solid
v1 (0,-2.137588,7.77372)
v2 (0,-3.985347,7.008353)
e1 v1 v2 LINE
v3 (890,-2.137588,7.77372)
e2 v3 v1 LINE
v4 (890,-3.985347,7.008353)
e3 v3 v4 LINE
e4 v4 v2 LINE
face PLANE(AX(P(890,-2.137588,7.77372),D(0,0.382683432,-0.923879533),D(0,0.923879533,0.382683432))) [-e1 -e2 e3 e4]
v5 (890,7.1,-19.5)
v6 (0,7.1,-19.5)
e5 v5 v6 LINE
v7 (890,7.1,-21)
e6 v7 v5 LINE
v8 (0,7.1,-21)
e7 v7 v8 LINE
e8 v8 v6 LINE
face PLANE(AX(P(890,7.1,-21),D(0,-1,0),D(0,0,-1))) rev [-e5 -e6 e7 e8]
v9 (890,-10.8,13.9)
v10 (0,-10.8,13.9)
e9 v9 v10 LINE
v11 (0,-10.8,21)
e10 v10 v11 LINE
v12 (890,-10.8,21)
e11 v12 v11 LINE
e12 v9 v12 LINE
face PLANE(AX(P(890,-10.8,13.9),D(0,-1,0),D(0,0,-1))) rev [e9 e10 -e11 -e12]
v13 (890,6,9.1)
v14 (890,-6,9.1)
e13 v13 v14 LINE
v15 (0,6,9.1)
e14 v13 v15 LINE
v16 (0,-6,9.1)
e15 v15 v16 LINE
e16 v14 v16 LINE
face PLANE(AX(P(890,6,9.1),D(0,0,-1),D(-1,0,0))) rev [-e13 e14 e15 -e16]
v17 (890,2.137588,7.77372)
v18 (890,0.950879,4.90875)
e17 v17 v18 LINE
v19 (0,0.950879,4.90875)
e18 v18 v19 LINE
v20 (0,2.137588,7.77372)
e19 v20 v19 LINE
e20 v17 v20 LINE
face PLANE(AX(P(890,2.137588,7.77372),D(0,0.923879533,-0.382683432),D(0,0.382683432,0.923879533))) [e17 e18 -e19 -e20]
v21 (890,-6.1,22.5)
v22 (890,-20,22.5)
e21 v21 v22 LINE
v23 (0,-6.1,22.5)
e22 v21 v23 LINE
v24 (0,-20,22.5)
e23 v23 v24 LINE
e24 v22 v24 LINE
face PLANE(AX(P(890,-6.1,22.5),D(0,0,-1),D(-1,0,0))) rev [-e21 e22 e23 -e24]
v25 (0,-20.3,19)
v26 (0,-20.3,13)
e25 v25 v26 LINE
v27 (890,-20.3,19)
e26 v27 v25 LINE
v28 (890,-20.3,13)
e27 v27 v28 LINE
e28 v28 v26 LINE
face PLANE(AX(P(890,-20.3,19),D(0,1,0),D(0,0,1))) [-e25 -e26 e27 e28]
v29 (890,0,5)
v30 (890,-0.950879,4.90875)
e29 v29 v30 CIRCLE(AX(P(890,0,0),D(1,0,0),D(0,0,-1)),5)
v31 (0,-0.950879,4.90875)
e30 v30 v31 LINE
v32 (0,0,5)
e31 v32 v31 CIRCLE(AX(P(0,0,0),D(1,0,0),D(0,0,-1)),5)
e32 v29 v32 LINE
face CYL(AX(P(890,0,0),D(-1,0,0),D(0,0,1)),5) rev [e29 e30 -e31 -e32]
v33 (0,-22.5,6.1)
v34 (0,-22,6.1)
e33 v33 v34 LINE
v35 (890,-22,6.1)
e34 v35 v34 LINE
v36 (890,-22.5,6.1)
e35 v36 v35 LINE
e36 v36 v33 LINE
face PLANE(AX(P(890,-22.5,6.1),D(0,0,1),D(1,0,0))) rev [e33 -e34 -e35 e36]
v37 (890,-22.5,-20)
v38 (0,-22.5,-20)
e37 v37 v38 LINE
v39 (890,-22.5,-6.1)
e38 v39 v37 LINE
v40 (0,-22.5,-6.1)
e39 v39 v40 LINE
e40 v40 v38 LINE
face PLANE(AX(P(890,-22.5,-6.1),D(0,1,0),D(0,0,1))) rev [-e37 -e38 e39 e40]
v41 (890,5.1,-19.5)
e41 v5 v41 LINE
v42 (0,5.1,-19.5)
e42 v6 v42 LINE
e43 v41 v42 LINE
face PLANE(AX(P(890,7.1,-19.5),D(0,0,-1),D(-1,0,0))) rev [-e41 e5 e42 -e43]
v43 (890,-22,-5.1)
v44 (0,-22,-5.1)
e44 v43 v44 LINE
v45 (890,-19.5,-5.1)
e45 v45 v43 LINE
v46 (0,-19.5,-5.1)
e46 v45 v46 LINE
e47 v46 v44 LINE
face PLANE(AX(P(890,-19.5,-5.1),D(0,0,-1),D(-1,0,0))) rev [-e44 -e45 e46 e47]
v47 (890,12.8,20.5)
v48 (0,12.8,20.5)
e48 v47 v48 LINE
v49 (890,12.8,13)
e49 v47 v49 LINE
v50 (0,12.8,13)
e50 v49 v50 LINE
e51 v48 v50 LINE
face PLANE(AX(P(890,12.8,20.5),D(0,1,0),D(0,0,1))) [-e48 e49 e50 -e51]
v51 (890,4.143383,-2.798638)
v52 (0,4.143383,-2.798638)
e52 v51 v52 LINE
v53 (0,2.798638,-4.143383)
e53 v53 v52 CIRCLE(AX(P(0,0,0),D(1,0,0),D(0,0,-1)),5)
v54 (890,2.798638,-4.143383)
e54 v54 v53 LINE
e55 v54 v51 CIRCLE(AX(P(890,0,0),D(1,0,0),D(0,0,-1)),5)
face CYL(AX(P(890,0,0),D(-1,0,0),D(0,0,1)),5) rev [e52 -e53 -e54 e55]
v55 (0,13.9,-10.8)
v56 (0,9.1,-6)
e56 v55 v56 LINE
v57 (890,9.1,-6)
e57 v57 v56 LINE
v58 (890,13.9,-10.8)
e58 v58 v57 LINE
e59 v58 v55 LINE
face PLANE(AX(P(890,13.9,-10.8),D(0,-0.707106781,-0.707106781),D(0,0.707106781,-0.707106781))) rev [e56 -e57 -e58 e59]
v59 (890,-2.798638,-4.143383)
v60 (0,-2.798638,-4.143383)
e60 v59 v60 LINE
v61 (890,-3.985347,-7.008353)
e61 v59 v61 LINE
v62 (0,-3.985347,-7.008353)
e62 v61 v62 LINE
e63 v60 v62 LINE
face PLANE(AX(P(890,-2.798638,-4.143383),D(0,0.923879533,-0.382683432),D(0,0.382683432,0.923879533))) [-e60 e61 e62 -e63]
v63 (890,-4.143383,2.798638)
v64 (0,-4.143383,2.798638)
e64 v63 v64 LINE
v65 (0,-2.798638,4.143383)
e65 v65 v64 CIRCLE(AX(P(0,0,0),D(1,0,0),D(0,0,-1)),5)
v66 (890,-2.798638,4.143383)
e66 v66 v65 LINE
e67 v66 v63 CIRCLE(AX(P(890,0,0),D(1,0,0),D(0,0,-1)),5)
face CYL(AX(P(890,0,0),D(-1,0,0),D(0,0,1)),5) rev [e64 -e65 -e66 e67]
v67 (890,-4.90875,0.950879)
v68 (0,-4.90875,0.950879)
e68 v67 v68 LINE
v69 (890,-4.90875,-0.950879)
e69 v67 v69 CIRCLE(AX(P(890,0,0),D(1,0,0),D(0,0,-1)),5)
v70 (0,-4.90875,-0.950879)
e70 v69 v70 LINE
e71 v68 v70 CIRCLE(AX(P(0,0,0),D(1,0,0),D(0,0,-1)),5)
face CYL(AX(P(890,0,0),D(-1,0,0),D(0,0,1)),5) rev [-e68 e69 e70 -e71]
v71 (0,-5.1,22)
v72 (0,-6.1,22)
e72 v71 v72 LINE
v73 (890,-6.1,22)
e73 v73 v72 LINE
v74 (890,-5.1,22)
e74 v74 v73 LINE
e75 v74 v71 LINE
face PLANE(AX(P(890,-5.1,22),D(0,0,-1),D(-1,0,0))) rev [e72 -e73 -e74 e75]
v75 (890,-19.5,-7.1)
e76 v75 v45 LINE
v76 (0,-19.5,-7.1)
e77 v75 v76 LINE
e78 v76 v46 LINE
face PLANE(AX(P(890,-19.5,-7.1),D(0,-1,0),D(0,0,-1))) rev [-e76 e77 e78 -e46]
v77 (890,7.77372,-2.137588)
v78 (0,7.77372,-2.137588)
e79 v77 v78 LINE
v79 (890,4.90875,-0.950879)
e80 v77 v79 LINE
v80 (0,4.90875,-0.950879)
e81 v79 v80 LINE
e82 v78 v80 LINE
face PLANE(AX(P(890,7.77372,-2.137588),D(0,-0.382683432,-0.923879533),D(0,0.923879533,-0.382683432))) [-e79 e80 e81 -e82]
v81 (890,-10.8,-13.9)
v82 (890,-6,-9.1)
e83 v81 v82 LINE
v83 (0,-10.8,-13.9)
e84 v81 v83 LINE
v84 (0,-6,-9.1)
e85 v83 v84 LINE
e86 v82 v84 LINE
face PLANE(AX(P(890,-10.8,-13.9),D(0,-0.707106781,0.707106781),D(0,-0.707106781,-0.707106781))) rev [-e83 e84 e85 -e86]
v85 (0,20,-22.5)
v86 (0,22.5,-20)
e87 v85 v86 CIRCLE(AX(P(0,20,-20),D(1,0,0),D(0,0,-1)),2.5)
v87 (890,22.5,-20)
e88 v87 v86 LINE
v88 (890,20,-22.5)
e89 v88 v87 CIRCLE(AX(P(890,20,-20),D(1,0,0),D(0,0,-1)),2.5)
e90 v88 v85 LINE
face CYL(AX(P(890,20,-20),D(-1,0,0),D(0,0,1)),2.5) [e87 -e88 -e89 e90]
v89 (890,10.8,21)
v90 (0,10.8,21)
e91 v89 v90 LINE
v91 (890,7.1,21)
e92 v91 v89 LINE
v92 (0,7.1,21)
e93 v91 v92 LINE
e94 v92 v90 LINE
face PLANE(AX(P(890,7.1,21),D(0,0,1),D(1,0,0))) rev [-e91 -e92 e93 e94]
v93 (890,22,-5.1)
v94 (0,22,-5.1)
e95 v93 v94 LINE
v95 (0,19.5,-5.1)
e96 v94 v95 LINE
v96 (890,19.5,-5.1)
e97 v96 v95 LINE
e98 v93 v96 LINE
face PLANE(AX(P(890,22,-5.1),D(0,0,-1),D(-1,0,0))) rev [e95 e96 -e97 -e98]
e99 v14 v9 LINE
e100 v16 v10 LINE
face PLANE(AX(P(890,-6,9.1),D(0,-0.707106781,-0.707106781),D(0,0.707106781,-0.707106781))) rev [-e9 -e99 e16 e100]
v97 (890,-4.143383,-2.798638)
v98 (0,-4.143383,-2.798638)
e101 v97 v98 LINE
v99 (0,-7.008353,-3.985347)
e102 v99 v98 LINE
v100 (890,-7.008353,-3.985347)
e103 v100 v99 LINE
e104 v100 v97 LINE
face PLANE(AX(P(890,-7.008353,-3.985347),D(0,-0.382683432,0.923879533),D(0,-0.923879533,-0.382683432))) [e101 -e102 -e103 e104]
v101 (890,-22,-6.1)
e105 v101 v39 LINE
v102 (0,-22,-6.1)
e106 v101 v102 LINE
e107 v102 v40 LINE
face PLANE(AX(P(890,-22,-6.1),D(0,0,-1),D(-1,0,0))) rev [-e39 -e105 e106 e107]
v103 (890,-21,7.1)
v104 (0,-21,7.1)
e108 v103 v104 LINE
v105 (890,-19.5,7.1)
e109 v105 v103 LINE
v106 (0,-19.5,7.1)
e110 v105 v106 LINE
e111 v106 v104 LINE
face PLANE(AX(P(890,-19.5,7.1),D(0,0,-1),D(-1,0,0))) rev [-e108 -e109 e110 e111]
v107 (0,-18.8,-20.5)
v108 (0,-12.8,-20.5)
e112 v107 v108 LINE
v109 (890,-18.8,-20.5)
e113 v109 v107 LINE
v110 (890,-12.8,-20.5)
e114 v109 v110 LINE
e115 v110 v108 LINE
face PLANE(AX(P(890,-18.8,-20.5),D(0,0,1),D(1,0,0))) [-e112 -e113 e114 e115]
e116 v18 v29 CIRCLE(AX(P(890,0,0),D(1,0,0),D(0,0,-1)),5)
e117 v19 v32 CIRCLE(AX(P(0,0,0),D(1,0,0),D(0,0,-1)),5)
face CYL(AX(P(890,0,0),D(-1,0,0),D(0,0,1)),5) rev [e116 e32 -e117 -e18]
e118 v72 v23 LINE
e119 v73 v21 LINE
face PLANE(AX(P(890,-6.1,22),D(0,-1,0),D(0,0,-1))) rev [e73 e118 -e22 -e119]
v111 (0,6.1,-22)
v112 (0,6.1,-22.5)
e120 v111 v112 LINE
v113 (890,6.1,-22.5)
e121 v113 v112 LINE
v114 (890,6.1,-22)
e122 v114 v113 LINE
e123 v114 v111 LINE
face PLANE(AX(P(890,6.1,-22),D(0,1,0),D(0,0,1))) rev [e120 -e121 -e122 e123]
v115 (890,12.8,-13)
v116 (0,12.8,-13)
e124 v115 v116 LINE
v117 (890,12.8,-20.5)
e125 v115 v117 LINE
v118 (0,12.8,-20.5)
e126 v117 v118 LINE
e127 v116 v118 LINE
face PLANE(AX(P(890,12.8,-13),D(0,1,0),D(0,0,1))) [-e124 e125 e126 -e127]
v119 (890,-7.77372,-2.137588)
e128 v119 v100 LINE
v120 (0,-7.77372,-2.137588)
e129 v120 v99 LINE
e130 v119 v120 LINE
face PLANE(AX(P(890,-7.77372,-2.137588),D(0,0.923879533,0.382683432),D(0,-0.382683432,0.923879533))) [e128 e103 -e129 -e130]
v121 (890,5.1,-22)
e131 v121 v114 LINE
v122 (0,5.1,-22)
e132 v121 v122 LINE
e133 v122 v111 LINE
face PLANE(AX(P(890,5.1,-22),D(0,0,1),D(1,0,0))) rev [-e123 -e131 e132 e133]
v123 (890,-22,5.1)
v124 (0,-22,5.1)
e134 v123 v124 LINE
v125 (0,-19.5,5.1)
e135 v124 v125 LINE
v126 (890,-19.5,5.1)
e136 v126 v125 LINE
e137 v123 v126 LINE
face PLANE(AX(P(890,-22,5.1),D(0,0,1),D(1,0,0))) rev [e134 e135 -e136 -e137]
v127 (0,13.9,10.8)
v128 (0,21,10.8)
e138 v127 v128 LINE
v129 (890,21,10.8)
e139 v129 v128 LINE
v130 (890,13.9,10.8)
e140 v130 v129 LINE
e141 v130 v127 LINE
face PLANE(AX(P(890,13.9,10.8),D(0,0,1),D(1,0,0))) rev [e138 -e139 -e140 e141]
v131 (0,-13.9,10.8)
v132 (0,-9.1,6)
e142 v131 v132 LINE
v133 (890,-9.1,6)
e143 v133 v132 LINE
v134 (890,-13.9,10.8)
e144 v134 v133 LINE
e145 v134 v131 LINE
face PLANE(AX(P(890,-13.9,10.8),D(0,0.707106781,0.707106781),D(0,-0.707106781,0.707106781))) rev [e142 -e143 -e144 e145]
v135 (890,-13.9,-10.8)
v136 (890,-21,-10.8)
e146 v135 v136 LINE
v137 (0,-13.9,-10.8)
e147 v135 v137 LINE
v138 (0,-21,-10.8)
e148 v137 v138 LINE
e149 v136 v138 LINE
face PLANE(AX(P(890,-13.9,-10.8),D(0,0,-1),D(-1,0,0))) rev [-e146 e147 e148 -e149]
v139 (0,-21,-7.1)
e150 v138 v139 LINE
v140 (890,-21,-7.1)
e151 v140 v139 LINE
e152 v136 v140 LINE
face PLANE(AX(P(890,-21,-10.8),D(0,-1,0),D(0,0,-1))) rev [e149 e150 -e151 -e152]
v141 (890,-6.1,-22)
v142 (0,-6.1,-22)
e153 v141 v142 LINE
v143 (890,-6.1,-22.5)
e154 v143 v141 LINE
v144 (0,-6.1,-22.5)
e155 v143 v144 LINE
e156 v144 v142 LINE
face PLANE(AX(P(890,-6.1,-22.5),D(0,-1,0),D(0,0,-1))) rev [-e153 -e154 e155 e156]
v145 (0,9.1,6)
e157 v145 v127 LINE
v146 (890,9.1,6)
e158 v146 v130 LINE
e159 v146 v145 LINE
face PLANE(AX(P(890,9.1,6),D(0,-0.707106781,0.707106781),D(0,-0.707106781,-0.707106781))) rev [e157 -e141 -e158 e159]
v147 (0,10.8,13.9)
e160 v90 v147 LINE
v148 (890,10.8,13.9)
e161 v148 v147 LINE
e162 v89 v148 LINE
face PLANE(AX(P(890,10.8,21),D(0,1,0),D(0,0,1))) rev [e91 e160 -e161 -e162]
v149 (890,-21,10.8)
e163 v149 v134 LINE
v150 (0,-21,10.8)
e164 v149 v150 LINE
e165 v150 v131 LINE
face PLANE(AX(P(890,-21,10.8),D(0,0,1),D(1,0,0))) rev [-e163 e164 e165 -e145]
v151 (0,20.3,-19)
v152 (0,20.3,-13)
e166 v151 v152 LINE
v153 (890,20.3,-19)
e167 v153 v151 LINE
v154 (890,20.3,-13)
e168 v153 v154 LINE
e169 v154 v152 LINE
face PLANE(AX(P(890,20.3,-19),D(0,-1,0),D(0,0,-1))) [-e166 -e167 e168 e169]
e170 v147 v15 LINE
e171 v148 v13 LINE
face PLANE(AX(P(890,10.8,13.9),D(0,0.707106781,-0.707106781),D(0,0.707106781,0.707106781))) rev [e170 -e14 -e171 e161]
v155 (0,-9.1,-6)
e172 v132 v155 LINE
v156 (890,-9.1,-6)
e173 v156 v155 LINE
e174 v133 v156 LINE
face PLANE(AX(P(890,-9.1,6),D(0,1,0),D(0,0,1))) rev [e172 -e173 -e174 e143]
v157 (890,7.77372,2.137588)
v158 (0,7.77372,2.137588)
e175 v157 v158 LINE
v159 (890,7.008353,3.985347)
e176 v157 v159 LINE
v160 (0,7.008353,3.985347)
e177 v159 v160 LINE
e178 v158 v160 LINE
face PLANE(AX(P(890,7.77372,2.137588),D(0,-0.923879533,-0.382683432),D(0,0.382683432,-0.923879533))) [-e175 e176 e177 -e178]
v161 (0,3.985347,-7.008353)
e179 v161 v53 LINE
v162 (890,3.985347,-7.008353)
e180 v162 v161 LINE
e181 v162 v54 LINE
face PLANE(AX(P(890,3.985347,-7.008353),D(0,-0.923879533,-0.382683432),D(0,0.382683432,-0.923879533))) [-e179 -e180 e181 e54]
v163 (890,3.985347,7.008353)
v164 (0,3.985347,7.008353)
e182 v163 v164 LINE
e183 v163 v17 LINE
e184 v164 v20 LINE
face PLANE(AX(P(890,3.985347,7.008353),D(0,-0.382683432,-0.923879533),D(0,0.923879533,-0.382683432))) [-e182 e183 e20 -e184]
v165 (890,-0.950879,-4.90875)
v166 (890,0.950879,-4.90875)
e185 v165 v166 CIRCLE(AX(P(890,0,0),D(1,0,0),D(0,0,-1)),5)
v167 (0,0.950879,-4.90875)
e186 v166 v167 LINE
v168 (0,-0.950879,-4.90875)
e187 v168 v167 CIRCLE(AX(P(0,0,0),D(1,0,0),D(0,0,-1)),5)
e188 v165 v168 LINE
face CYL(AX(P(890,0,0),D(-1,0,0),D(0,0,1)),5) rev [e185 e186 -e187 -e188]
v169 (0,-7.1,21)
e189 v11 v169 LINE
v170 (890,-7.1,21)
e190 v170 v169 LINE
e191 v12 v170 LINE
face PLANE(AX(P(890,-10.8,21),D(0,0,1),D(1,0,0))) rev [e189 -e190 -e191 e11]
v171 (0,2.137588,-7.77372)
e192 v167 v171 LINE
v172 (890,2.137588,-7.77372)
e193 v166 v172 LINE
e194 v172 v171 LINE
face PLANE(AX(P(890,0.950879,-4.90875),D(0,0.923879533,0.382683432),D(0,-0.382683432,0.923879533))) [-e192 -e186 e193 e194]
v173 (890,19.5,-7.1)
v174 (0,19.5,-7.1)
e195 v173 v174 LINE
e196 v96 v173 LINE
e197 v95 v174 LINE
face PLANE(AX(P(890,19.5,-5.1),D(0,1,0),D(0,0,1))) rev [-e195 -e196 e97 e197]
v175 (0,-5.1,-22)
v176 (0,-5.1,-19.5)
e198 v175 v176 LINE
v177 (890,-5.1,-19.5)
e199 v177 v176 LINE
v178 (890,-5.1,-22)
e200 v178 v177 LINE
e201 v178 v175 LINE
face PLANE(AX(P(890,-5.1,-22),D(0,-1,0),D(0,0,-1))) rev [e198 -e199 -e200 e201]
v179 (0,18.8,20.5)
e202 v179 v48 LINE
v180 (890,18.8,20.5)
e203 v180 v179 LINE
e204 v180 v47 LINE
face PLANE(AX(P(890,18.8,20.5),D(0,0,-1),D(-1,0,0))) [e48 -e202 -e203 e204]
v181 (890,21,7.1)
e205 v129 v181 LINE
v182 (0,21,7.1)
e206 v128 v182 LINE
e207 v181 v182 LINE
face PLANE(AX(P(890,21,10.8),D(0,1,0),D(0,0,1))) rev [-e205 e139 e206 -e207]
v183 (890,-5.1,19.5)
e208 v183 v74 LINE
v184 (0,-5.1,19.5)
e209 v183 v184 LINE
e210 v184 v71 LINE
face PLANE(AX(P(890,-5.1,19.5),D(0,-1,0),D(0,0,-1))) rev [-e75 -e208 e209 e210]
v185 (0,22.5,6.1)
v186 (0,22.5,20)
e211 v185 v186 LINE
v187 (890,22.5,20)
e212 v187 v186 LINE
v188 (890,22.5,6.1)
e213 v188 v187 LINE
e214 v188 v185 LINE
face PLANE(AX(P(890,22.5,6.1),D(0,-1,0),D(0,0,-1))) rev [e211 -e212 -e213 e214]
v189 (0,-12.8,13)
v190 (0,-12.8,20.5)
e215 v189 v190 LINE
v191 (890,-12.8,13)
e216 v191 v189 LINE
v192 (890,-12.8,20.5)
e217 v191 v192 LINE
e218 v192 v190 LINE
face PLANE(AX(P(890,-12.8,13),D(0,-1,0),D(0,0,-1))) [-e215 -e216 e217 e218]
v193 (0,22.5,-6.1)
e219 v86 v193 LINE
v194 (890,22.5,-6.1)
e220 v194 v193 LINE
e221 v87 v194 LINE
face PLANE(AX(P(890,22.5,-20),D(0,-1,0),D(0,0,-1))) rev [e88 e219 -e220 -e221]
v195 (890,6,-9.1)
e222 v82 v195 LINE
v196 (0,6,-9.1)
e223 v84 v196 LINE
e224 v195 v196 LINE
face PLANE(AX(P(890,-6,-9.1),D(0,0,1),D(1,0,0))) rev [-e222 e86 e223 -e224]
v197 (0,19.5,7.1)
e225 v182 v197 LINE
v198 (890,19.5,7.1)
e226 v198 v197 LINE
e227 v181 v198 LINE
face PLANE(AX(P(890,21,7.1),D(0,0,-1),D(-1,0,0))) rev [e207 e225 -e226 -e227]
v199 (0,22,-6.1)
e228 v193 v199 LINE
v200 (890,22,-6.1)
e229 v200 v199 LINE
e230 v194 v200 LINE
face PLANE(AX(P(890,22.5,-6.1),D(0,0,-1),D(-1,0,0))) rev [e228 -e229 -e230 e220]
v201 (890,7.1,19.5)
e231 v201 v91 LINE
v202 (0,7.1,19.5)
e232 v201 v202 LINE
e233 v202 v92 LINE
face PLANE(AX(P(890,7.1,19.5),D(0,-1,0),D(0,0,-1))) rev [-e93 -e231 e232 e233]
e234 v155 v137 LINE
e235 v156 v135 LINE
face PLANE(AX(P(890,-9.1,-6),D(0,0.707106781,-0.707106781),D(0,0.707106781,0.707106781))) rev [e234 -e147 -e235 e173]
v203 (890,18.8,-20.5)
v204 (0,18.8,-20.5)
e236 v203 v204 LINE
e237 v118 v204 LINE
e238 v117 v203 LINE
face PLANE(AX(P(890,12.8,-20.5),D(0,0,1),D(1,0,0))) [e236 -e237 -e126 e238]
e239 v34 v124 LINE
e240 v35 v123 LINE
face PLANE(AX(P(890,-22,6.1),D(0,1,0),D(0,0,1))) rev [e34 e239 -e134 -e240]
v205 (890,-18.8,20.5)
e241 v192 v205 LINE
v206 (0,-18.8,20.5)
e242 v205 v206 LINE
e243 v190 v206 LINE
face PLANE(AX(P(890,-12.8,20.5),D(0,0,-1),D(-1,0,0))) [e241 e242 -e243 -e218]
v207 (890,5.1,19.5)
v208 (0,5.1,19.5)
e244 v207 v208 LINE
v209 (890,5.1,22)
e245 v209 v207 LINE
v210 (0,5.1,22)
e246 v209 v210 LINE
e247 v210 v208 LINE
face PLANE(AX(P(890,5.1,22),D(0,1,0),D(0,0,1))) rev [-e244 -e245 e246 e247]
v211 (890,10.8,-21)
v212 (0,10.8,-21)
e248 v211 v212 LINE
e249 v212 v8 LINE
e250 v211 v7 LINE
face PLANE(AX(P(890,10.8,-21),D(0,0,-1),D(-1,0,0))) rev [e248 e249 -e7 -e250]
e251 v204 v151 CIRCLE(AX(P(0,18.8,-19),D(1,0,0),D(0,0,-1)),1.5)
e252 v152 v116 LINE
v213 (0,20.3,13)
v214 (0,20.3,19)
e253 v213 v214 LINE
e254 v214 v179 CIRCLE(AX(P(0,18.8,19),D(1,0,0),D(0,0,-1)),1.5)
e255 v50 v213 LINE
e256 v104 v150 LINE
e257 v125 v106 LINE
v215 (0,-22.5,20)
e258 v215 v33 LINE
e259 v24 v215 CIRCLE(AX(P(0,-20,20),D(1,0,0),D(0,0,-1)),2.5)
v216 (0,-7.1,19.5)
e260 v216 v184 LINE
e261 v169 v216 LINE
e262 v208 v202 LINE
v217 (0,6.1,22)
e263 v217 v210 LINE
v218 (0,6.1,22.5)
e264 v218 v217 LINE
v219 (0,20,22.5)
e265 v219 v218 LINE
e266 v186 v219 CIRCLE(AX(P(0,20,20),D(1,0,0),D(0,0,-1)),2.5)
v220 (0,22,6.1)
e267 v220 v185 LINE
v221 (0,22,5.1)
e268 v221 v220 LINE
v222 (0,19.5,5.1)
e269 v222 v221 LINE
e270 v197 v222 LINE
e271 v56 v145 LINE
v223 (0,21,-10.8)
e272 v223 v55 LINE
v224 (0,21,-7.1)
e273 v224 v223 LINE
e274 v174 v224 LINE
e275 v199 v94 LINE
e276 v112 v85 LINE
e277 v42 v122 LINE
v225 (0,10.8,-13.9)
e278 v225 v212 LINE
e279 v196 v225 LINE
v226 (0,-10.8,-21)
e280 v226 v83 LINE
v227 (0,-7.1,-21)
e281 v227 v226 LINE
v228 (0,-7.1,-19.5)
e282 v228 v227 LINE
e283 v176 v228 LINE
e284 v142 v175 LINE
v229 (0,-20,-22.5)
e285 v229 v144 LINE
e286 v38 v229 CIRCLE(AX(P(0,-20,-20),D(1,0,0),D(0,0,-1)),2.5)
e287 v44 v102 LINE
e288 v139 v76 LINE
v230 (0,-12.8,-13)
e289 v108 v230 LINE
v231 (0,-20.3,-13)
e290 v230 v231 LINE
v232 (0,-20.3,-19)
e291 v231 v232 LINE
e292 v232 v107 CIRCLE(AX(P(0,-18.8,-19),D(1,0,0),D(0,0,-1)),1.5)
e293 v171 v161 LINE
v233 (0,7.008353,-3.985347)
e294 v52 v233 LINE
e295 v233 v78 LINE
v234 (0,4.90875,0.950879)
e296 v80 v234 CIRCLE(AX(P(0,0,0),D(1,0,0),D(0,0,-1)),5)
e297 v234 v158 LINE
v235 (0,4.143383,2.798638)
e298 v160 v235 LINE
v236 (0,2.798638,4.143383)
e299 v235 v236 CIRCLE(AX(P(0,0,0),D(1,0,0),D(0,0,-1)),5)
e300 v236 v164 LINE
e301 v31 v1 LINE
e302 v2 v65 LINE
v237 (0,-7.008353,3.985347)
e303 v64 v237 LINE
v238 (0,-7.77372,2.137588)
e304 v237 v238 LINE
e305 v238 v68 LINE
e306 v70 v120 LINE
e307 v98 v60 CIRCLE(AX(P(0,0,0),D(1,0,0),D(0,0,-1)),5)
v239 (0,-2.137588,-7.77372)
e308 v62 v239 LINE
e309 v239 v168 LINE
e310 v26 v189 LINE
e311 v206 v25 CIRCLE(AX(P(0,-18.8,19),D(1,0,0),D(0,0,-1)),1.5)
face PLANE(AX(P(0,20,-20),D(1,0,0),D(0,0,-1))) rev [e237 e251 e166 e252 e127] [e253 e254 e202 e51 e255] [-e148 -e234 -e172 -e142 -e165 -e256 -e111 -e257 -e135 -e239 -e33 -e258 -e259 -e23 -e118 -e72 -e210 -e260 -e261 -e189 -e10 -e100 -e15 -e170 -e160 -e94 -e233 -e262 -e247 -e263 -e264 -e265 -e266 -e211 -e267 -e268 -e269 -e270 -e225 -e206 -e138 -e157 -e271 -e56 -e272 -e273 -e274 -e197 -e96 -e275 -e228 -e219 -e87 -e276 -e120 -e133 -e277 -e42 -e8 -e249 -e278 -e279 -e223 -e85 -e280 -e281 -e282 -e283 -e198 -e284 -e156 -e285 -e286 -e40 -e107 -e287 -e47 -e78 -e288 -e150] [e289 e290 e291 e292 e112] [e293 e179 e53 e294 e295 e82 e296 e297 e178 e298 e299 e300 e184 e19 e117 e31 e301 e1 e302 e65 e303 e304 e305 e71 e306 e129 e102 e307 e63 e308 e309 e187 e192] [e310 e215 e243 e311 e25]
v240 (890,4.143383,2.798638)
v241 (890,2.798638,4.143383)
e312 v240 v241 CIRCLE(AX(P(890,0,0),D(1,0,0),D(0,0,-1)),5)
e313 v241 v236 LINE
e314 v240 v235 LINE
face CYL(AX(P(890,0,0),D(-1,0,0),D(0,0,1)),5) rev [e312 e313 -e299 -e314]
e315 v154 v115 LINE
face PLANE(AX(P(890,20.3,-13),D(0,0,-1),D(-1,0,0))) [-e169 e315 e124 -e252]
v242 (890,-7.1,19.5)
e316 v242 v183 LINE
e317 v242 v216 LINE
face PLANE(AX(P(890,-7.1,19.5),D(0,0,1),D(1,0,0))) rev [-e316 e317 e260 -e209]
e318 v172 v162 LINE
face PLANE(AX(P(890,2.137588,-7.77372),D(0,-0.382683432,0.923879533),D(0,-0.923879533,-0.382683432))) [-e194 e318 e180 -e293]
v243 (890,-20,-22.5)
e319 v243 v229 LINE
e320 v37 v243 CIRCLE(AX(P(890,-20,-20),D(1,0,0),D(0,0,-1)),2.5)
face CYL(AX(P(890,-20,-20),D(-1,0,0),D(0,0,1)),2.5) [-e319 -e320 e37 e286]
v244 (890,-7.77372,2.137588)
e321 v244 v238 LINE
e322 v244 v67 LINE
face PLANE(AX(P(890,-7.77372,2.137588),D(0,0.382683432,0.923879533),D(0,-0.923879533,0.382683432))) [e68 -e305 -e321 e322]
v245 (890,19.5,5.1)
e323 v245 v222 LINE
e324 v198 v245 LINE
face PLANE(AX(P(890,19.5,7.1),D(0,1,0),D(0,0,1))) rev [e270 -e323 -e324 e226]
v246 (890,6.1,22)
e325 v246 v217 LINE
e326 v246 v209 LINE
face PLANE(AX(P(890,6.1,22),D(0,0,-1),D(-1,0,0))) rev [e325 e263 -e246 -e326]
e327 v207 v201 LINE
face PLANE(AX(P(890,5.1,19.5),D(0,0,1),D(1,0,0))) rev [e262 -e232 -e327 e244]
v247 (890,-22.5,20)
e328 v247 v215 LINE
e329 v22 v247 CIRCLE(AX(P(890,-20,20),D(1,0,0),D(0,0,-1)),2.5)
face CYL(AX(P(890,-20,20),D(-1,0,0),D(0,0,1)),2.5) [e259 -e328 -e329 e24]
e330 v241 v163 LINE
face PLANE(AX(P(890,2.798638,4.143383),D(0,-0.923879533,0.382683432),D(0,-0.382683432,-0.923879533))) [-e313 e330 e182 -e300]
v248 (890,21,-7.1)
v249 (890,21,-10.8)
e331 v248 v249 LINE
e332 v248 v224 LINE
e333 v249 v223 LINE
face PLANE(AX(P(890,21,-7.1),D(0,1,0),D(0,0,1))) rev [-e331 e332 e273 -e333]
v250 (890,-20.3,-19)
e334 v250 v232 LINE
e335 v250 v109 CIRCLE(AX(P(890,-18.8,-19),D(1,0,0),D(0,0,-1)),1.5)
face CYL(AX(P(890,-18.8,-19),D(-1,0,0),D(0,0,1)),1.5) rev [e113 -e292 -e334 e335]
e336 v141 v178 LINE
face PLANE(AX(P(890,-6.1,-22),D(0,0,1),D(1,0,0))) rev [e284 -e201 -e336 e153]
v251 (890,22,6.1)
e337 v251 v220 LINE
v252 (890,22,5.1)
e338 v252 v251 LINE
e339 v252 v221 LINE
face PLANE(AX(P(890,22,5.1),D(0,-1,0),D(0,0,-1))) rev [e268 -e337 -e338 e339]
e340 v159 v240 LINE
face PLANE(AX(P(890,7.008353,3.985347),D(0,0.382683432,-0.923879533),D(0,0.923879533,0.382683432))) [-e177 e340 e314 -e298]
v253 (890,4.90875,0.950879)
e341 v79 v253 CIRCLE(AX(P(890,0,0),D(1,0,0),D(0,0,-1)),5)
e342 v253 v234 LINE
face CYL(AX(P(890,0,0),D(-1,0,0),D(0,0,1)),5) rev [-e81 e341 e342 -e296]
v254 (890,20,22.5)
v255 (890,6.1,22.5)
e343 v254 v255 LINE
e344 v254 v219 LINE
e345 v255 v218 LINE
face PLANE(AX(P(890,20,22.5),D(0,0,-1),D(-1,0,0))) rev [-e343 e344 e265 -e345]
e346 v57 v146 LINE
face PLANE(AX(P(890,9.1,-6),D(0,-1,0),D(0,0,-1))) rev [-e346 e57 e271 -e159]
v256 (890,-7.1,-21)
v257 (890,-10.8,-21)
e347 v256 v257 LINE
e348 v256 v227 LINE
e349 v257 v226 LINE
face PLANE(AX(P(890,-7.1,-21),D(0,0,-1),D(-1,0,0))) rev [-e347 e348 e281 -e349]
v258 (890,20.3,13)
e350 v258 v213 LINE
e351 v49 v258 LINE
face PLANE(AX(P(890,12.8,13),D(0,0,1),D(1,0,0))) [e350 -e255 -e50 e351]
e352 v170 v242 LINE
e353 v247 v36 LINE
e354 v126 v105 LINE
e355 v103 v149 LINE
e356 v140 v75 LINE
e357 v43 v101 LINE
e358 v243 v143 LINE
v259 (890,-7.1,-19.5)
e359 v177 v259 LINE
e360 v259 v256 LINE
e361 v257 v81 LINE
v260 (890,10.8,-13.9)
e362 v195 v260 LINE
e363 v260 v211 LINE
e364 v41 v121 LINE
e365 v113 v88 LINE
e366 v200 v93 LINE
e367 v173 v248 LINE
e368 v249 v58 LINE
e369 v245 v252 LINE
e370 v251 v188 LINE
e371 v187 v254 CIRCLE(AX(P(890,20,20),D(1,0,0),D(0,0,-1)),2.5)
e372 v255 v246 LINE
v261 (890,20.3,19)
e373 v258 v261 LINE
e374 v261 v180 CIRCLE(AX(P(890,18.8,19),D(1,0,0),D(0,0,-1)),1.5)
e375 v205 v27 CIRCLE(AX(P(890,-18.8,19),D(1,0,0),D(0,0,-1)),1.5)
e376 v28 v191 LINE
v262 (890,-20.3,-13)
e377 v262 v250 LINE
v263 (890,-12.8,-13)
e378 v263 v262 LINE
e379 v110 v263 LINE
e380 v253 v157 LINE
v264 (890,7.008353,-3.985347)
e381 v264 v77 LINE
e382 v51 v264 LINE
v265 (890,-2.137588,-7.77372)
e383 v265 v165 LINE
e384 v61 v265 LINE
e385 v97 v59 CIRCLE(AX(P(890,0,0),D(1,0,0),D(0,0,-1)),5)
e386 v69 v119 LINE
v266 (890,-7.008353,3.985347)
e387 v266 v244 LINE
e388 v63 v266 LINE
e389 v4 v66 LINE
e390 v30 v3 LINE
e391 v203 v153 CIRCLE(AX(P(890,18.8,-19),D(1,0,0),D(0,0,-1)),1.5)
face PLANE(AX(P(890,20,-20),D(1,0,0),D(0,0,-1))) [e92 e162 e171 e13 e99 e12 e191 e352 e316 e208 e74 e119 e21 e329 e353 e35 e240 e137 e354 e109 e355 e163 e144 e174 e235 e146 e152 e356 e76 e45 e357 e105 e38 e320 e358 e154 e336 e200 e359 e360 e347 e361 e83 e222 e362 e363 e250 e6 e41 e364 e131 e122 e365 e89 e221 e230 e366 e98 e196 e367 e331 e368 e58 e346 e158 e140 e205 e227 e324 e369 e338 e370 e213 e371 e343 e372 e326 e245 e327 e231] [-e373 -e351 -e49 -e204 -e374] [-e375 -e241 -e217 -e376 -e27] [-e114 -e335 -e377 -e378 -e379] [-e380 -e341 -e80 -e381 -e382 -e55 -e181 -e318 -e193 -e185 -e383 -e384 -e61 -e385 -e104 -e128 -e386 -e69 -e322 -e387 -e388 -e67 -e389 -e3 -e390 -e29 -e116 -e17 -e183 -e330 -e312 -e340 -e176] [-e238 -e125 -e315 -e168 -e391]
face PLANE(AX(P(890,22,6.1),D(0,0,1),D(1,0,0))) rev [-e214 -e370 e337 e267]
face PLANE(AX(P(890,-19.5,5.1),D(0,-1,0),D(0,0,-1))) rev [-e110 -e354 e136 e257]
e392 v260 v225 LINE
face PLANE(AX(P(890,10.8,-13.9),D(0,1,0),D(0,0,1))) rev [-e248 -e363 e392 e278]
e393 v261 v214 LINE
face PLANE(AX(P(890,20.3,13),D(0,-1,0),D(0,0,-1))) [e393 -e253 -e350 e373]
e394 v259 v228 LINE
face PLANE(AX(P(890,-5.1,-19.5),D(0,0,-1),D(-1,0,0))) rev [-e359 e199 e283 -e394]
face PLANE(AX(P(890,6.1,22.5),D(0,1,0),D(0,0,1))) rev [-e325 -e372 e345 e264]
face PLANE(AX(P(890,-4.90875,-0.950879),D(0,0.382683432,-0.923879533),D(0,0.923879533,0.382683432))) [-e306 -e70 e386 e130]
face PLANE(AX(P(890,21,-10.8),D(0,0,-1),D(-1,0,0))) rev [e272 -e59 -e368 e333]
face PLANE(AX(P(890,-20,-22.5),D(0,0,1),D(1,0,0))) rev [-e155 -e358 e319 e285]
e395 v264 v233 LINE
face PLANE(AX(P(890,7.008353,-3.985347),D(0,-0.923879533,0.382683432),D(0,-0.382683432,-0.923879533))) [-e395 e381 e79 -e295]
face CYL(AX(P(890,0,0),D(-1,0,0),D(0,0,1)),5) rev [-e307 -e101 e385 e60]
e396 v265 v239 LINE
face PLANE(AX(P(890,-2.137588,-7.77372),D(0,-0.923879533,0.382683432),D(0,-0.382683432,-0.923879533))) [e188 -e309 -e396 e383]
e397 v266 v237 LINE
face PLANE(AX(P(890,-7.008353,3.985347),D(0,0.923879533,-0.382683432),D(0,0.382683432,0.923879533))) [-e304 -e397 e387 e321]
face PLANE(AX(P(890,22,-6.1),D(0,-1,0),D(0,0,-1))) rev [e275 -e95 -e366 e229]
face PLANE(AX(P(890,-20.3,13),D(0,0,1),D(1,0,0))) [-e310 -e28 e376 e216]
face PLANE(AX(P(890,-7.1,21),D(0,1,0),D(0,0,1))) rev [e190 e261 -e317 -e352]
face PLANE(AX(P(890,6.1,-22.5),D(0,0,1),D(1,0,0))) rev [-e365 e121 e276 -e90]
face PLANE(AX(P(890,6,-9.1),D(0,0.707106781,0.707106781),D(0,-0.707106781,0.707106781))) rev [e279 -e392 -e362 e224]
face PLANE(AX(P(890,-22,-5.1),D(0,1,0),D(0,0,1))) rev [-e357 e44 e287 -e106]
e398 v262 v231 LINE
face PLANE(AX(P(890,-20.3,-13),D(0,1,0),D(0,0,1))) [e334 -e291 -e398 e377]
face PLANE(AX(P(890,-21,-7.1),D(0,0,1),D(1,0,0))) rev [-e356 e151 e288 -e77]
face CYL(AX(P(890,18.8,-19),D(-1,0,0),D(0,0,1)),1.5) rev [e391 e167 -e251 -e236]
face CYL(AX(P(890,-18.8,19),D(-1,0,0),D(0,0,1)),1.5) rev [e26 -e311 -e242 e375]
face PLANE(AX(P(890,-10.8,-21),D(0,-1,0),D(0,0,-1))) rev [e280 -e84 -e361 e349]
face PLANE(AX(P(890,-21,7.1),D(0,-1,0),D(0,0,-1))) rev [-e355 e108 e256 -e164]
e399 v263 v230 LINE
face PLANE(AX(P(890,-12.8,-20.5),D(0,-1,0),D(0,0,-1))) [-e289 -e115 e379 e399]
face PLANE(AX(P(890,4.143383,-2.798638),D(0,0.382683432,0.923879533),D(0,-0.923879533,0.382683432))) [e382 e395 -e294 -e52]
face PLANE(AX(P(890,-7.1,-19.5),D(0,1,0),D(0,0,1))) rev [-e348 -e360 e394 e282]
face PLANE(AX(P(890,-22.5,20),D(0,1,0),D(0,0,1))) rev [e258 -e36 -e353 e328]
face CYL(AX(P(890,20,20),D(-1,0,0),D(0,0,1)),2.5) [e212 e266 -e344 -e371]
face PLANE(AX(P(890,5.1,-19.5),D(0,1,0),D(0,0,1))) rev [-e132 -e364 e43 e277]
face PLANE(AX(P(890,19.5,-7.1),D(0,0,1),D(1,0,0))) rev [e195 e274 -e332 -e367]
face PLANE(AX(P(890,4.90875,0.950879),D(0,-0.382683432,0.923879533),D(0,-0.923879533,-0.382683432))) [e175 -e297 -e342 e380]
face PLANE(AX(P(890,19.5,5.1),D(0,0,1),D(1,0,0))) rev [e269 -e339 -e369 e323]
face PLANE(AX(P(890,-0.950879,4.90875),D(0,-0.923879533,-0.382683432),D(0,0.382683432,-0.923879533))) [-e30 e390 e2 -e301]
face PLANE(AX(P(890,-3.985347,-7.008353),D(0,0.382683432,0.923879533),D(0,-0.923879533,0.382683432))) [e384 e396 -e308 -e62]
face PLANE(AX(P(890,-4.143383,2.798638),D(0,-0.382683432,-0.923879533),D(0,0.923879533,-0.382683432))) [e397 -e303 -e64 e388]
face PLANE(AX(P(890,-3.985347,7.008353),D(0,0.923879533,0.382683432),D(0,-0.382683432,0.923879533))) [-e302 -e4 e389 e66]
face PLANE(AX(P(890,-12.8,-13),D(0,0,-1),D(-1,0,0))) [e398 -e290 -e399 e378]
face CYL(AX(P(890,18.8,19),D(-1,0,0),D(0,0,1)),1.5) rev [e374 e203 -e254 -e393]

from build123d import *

# Parameters (mm, degrees)
ALUMINUM_PROFILE_45_X_45L_X_R2_5_1_DEPTH = 890


with BuildPart() as part:
    # Sketch1 → Aluminum Profile 45 X 45L X R2.5(1) (new body)
    with BuildSketch(Plane.YZ):
        with BuildLine():
            Line((6.1, -22.5), (20, -22.5))
            ThreePointArc((20, -22.5), (21.767766953, -21.767766953), (22.5, -20))
            Line((22.5, -20), (22.5, -6.1))
            Line((22.5, -6.1), (22, -6.1))
            Line((22, -6.1), (22, -5.1))
            Line((22, -5.1), (19.5, -5.1))
            Line((19.5, -5.1), (19.5, -7.1))
            Line((19.5, -7.1), (21, -7.1))
            Line((21, -7.1), (21, -10.8))
            Line((21, -10.8), (13.9, -10.8))
            Line((13.9, -10.8), (9.1, -6))
            Line((9.1, -6), (9.1, 6))
            Line((9.1, 6), (13.9, 10.8))
            Line((13.9, 10.8), (21, 10.8))
            Line((21, 10.8), (21, 7.1))
            Line((21, 7.1), (19.5, 7.1))
            Line((19.5, 7.1), (19.5, 5.1))
            Line((19.5, 5.1), (22, 5.1))
            Line((22, 5.1), (22, 6.1))
            Line((22, 6.1), (22.5, 6.1))
            Line((22.5, 6.1), (22.5, 20))
            ThreePointArc((22.5, 20), (21.767766953, 21.767766953), (20, 22.5))
            Line((20, 22.5), (6.1, 22.5))
            Line((6.1, 22.5), (6.1, 22))
            Line((6.1, 22), (5.1, 22))
            Line((5.1, 22), (5.1, 19.5))
            Line((5.1, 19.5), (7.1, 19.5))
            Line((7.1, 19.5), (7.1, 21))
            Line((7.1, 21), (10.8, 21))
            Line((10.8, 21), (10.8, 13.9))
            Line((10.8, 13.9), (6, 9.1))
            Line((6, 9.1), (-6, 9.1))
            Line((-6, 9.1), (-10.8, 13.9))
            Line((-10.8, 13.9), (-10.8, 21))
            Line((-10.8, 21), (-7.1, 21))
            Line((-7.1, 21), (-7.1, 19.5))
            Line((-7.1, 19.5), (-5.1, 19.5))
            Line((-5.1, 19.5), (-5.1, 22))
            Line((-5.1, 22), (-6.1, 22))
            Line((-6.1, 22), (-6.1, 22.5))
            Line((-6.1, 22.5), (-20, 22.5))
            ThreePointArc((-20, 22.5), (-21.767766953, 21.767766953), (-22.5, 20))
            Line((-22.5, 20), (-22.5, 6.1))
            Line((-22.5, 6.1), (-22, 6.1))
            Line((-22, 6.1), (-22, 5.1))
            Line((-22, 5.1), (-19.5, 5.1))
            Line((-19.5, 5.1), (-19.5, 7.1))
            Line((-19.5, 7.1), (-21, 7.1))
            Line((-21, 7.1), (-21, 10.8))
            Line((-21, 10.8), (-13.9, 10.8))
            Line((-13.9, 10.8), (-9.1, 6))
            Line((-9.1, 6), (-9.1, -6))
            Line((-9.1, -6), (-13.9, -10.8))
            Line((-13.9, -10.8), (-21, -10.8))
            Line((-21, -10.8), (-21, -7.1))
            Line((-21, -7.1), (-19.5, -7.1))
            Line((-19.5, -7.1), (-19.5, -5.1))
            Line((-19.5, -5.1), (-22, -5.1))
            Line((-22, -5.1), (-22, -6.1))
            Line((-22, -6.1), (-22.5, -6.1))
            Line((-22.5, -6.1), (-22.5, -20))
            ThreePointArc((-22.5, -20), (-21.767766953, -21.767766953), (-20, -22.5))
            Line((-20, -22.5), (-6.1, -22.5))
            Line((-6.1, -22.5), (-6.1, -22))
            Line((-6.1, -22), (-5.1, -22))
            Line((-5.1, -22), (-5.1, -19.5))
            Line((-5.1, -19.5), (-7.1, -19.5))
            Line((-7.1, -19.5), (-7.1, -21))
            Line((-7.1, -21), (-10.8, -21))
            Line((-10.8, -21), (-10.8, -13.9))
            Line((-10.8, -13.9), (-6, -9.1))
            Line((-6, -9.1), (6, -9.1))
            Line((6, -9.1), (10.8, -13.9))
            Line((10.8, -13.9), (10.8, -21))
            Line((10.8, -21), (7.1, -21))
            Line((7.1, -21), (7.1, -19.5))
            Line((7.1, -19.5), (5.1, -19.5))
            Line((5.1, -19.5), (5.1, -22))
            Line((5.1, -22), (6.1, -22))
            Line((6.1, -22), (6.1, -22.5))
        make_face()
        with BuildLine():
            Line((-12.8, 20.5), (-18.8, 20.5))
            ThreePointArc((-18.8, 20.5), (-19.860660172, 20.060660172), (-20.3, 19))
            Line((-20.3, 19), (-20.3, 13))
            Line((-20.3, 13), (-12.8, 13))
            Line((-12.8, 13), (-12.8, 20.5))
        make_face(mode=Mode.SUBTRACT)
        with BuildLine():
            Line((-20.3, -13), (-20.3, -19))
            ThreePointArc((-20.3, -19), (-19.860660172, -20.060660172), (-18.8, -20.5))
            Line((-18.8, -20.5), (-12.8, -20.5))
            Line((-12.8, -20.5), (-12.8, -13))
            Line((-12.8, -13), (-20.3, -13))
        make_face(mode=Mode.SUBTRACT)
        with BuildLine():
            Line((7.008352828, 3.985346991), (4.143383445, 2.798637817))
            ThreePointArc((4.143383445, 2.798637817), (3.535533906, 3.535533906), (2.798637817, 4.143383445))
            Line((2.798637817, 4.143383445), (3.985346991, 7.008352828))
            Line((3.985346991, 7.008352828), (2.137587926, 7.773719692))
            Line((2.137587926, 7.773719692), (0.950878752, 4.908750309))
            ThreePointArc((0.950878752, 4.908750309), (0, 5), (-0.950878752, 4.908750309))
            Line((-0.950878752, 4.908750309), (-2.137587926, 7.773719692))
            Line((-2.137587926, 7.773719692), (-3.985346991, 7.008352828))
            Line((-3.985346991, 7.008352828), (-2.798637817, 4.143383445))
            ThreePointArc((-2.798637817, 4.143383445), (-3.535533906, 3.535533906), (-4.143383445, 2.798637817))
            Line((-4.143383445, 2.798637817), (-7.008352828, 3.985346991))
            Line((-7.008352828, 3.985346991), (-7.773719692, 2.137587926))
            Line((-7.773719692, 2.137587926), (-4.908750309, 0.950878752))
            ThreePointArc((-4.908750309, 0.950878752), (-5, 0), (-4.908750309, -0.950878752))
            Line((-4.908750309, -0.950878752), (-7.773719692, -2.137587926))
            Line((-7.773719692, -2.137587926), (-7.008352828, -3.985346991))
            Line((-7.008352828, -3.985346991), (-4.143383445, -2.798637817))
            ThreePointArc((-4.143383445, -2.798637817), (-3.535533906, -3.535533906), (-2.798637817, -4.143383445))
            Line((-2.798637817, -4.143383445), (-3.985346991, -7.008352828))
            Line((-3.985346991, -7.008352828), (-2.137587926, -7.773719692))
            Line((-2.137587926, -7.773719692), (-0.950878752, -4.908750309))
            ThreePointArc((-0.950878752, -4.908750309), (0, -5), (0.950878752, -4.908750309))
            Line((0.950878752, -4.908750309), (2.137587926, -7.773719692))
            Line((2.137587926, -7.773719692), (3.985346991, -7.008352828))
            Line((3.985346991, -7.008352828), (2.798637817, -4.143383445))
            ThreePointArc((2.798637817, -4.143383445), (3.535533906, -3.535533906), (4.143383445, -2.798637817))
            Line((4.143383445, -2.798637817), (7.008352828, -3.985346991))
            Line((7.008352828, -3.985346991), (7.773719692, -2.137587926))
            Line((7.773719692, -2.137587926), (4.908750309, -0.950878752))
            ThreePointArc((4.908750309, -0.950878752), (5, 0), (4.908750309, 0.950878752))
            Line((4.908750309, 0.950878752), (7.773719692, 2.137587926))
            Line((7.773719692, 2.137587926), (7.008352828, 3.985346991))
        make_face(mode=Mode.SUBTRACT)
        with BuildLine():
            Line((20.3, -19), (20.3, -13))
            Line((20.3, -13), (12.8, -13))
            Line((12.8, -13), (12.8, -20.5))
            Line((12.8, -20.5), (18.8, -20.5))
            ThreePointArc((18.8, -20.5), (19.860660172, -20.060660172), (20.3, -19))
        make_face(mode=Mode.SUBTRACT)
        with BuildLine():
            Line((20.3, 13), (20.3, 19))
            ThreePointArc((20.3, 19), (19.860660172, 20.060660172), (18.8, 20.5))
            Line((18.8, 20.5), (12.8, 20.5))
            Line((12.8, 20.5), (12.8, 13))
            Line((12.8, 13), (20.3, 13))
        make_face(mode=Mode.SUBTRACT)
    extrude(amount=ALUMINUM_PROFILE_45_X_45L_X_R2_5_1_DEPTH)


solid = part.part
